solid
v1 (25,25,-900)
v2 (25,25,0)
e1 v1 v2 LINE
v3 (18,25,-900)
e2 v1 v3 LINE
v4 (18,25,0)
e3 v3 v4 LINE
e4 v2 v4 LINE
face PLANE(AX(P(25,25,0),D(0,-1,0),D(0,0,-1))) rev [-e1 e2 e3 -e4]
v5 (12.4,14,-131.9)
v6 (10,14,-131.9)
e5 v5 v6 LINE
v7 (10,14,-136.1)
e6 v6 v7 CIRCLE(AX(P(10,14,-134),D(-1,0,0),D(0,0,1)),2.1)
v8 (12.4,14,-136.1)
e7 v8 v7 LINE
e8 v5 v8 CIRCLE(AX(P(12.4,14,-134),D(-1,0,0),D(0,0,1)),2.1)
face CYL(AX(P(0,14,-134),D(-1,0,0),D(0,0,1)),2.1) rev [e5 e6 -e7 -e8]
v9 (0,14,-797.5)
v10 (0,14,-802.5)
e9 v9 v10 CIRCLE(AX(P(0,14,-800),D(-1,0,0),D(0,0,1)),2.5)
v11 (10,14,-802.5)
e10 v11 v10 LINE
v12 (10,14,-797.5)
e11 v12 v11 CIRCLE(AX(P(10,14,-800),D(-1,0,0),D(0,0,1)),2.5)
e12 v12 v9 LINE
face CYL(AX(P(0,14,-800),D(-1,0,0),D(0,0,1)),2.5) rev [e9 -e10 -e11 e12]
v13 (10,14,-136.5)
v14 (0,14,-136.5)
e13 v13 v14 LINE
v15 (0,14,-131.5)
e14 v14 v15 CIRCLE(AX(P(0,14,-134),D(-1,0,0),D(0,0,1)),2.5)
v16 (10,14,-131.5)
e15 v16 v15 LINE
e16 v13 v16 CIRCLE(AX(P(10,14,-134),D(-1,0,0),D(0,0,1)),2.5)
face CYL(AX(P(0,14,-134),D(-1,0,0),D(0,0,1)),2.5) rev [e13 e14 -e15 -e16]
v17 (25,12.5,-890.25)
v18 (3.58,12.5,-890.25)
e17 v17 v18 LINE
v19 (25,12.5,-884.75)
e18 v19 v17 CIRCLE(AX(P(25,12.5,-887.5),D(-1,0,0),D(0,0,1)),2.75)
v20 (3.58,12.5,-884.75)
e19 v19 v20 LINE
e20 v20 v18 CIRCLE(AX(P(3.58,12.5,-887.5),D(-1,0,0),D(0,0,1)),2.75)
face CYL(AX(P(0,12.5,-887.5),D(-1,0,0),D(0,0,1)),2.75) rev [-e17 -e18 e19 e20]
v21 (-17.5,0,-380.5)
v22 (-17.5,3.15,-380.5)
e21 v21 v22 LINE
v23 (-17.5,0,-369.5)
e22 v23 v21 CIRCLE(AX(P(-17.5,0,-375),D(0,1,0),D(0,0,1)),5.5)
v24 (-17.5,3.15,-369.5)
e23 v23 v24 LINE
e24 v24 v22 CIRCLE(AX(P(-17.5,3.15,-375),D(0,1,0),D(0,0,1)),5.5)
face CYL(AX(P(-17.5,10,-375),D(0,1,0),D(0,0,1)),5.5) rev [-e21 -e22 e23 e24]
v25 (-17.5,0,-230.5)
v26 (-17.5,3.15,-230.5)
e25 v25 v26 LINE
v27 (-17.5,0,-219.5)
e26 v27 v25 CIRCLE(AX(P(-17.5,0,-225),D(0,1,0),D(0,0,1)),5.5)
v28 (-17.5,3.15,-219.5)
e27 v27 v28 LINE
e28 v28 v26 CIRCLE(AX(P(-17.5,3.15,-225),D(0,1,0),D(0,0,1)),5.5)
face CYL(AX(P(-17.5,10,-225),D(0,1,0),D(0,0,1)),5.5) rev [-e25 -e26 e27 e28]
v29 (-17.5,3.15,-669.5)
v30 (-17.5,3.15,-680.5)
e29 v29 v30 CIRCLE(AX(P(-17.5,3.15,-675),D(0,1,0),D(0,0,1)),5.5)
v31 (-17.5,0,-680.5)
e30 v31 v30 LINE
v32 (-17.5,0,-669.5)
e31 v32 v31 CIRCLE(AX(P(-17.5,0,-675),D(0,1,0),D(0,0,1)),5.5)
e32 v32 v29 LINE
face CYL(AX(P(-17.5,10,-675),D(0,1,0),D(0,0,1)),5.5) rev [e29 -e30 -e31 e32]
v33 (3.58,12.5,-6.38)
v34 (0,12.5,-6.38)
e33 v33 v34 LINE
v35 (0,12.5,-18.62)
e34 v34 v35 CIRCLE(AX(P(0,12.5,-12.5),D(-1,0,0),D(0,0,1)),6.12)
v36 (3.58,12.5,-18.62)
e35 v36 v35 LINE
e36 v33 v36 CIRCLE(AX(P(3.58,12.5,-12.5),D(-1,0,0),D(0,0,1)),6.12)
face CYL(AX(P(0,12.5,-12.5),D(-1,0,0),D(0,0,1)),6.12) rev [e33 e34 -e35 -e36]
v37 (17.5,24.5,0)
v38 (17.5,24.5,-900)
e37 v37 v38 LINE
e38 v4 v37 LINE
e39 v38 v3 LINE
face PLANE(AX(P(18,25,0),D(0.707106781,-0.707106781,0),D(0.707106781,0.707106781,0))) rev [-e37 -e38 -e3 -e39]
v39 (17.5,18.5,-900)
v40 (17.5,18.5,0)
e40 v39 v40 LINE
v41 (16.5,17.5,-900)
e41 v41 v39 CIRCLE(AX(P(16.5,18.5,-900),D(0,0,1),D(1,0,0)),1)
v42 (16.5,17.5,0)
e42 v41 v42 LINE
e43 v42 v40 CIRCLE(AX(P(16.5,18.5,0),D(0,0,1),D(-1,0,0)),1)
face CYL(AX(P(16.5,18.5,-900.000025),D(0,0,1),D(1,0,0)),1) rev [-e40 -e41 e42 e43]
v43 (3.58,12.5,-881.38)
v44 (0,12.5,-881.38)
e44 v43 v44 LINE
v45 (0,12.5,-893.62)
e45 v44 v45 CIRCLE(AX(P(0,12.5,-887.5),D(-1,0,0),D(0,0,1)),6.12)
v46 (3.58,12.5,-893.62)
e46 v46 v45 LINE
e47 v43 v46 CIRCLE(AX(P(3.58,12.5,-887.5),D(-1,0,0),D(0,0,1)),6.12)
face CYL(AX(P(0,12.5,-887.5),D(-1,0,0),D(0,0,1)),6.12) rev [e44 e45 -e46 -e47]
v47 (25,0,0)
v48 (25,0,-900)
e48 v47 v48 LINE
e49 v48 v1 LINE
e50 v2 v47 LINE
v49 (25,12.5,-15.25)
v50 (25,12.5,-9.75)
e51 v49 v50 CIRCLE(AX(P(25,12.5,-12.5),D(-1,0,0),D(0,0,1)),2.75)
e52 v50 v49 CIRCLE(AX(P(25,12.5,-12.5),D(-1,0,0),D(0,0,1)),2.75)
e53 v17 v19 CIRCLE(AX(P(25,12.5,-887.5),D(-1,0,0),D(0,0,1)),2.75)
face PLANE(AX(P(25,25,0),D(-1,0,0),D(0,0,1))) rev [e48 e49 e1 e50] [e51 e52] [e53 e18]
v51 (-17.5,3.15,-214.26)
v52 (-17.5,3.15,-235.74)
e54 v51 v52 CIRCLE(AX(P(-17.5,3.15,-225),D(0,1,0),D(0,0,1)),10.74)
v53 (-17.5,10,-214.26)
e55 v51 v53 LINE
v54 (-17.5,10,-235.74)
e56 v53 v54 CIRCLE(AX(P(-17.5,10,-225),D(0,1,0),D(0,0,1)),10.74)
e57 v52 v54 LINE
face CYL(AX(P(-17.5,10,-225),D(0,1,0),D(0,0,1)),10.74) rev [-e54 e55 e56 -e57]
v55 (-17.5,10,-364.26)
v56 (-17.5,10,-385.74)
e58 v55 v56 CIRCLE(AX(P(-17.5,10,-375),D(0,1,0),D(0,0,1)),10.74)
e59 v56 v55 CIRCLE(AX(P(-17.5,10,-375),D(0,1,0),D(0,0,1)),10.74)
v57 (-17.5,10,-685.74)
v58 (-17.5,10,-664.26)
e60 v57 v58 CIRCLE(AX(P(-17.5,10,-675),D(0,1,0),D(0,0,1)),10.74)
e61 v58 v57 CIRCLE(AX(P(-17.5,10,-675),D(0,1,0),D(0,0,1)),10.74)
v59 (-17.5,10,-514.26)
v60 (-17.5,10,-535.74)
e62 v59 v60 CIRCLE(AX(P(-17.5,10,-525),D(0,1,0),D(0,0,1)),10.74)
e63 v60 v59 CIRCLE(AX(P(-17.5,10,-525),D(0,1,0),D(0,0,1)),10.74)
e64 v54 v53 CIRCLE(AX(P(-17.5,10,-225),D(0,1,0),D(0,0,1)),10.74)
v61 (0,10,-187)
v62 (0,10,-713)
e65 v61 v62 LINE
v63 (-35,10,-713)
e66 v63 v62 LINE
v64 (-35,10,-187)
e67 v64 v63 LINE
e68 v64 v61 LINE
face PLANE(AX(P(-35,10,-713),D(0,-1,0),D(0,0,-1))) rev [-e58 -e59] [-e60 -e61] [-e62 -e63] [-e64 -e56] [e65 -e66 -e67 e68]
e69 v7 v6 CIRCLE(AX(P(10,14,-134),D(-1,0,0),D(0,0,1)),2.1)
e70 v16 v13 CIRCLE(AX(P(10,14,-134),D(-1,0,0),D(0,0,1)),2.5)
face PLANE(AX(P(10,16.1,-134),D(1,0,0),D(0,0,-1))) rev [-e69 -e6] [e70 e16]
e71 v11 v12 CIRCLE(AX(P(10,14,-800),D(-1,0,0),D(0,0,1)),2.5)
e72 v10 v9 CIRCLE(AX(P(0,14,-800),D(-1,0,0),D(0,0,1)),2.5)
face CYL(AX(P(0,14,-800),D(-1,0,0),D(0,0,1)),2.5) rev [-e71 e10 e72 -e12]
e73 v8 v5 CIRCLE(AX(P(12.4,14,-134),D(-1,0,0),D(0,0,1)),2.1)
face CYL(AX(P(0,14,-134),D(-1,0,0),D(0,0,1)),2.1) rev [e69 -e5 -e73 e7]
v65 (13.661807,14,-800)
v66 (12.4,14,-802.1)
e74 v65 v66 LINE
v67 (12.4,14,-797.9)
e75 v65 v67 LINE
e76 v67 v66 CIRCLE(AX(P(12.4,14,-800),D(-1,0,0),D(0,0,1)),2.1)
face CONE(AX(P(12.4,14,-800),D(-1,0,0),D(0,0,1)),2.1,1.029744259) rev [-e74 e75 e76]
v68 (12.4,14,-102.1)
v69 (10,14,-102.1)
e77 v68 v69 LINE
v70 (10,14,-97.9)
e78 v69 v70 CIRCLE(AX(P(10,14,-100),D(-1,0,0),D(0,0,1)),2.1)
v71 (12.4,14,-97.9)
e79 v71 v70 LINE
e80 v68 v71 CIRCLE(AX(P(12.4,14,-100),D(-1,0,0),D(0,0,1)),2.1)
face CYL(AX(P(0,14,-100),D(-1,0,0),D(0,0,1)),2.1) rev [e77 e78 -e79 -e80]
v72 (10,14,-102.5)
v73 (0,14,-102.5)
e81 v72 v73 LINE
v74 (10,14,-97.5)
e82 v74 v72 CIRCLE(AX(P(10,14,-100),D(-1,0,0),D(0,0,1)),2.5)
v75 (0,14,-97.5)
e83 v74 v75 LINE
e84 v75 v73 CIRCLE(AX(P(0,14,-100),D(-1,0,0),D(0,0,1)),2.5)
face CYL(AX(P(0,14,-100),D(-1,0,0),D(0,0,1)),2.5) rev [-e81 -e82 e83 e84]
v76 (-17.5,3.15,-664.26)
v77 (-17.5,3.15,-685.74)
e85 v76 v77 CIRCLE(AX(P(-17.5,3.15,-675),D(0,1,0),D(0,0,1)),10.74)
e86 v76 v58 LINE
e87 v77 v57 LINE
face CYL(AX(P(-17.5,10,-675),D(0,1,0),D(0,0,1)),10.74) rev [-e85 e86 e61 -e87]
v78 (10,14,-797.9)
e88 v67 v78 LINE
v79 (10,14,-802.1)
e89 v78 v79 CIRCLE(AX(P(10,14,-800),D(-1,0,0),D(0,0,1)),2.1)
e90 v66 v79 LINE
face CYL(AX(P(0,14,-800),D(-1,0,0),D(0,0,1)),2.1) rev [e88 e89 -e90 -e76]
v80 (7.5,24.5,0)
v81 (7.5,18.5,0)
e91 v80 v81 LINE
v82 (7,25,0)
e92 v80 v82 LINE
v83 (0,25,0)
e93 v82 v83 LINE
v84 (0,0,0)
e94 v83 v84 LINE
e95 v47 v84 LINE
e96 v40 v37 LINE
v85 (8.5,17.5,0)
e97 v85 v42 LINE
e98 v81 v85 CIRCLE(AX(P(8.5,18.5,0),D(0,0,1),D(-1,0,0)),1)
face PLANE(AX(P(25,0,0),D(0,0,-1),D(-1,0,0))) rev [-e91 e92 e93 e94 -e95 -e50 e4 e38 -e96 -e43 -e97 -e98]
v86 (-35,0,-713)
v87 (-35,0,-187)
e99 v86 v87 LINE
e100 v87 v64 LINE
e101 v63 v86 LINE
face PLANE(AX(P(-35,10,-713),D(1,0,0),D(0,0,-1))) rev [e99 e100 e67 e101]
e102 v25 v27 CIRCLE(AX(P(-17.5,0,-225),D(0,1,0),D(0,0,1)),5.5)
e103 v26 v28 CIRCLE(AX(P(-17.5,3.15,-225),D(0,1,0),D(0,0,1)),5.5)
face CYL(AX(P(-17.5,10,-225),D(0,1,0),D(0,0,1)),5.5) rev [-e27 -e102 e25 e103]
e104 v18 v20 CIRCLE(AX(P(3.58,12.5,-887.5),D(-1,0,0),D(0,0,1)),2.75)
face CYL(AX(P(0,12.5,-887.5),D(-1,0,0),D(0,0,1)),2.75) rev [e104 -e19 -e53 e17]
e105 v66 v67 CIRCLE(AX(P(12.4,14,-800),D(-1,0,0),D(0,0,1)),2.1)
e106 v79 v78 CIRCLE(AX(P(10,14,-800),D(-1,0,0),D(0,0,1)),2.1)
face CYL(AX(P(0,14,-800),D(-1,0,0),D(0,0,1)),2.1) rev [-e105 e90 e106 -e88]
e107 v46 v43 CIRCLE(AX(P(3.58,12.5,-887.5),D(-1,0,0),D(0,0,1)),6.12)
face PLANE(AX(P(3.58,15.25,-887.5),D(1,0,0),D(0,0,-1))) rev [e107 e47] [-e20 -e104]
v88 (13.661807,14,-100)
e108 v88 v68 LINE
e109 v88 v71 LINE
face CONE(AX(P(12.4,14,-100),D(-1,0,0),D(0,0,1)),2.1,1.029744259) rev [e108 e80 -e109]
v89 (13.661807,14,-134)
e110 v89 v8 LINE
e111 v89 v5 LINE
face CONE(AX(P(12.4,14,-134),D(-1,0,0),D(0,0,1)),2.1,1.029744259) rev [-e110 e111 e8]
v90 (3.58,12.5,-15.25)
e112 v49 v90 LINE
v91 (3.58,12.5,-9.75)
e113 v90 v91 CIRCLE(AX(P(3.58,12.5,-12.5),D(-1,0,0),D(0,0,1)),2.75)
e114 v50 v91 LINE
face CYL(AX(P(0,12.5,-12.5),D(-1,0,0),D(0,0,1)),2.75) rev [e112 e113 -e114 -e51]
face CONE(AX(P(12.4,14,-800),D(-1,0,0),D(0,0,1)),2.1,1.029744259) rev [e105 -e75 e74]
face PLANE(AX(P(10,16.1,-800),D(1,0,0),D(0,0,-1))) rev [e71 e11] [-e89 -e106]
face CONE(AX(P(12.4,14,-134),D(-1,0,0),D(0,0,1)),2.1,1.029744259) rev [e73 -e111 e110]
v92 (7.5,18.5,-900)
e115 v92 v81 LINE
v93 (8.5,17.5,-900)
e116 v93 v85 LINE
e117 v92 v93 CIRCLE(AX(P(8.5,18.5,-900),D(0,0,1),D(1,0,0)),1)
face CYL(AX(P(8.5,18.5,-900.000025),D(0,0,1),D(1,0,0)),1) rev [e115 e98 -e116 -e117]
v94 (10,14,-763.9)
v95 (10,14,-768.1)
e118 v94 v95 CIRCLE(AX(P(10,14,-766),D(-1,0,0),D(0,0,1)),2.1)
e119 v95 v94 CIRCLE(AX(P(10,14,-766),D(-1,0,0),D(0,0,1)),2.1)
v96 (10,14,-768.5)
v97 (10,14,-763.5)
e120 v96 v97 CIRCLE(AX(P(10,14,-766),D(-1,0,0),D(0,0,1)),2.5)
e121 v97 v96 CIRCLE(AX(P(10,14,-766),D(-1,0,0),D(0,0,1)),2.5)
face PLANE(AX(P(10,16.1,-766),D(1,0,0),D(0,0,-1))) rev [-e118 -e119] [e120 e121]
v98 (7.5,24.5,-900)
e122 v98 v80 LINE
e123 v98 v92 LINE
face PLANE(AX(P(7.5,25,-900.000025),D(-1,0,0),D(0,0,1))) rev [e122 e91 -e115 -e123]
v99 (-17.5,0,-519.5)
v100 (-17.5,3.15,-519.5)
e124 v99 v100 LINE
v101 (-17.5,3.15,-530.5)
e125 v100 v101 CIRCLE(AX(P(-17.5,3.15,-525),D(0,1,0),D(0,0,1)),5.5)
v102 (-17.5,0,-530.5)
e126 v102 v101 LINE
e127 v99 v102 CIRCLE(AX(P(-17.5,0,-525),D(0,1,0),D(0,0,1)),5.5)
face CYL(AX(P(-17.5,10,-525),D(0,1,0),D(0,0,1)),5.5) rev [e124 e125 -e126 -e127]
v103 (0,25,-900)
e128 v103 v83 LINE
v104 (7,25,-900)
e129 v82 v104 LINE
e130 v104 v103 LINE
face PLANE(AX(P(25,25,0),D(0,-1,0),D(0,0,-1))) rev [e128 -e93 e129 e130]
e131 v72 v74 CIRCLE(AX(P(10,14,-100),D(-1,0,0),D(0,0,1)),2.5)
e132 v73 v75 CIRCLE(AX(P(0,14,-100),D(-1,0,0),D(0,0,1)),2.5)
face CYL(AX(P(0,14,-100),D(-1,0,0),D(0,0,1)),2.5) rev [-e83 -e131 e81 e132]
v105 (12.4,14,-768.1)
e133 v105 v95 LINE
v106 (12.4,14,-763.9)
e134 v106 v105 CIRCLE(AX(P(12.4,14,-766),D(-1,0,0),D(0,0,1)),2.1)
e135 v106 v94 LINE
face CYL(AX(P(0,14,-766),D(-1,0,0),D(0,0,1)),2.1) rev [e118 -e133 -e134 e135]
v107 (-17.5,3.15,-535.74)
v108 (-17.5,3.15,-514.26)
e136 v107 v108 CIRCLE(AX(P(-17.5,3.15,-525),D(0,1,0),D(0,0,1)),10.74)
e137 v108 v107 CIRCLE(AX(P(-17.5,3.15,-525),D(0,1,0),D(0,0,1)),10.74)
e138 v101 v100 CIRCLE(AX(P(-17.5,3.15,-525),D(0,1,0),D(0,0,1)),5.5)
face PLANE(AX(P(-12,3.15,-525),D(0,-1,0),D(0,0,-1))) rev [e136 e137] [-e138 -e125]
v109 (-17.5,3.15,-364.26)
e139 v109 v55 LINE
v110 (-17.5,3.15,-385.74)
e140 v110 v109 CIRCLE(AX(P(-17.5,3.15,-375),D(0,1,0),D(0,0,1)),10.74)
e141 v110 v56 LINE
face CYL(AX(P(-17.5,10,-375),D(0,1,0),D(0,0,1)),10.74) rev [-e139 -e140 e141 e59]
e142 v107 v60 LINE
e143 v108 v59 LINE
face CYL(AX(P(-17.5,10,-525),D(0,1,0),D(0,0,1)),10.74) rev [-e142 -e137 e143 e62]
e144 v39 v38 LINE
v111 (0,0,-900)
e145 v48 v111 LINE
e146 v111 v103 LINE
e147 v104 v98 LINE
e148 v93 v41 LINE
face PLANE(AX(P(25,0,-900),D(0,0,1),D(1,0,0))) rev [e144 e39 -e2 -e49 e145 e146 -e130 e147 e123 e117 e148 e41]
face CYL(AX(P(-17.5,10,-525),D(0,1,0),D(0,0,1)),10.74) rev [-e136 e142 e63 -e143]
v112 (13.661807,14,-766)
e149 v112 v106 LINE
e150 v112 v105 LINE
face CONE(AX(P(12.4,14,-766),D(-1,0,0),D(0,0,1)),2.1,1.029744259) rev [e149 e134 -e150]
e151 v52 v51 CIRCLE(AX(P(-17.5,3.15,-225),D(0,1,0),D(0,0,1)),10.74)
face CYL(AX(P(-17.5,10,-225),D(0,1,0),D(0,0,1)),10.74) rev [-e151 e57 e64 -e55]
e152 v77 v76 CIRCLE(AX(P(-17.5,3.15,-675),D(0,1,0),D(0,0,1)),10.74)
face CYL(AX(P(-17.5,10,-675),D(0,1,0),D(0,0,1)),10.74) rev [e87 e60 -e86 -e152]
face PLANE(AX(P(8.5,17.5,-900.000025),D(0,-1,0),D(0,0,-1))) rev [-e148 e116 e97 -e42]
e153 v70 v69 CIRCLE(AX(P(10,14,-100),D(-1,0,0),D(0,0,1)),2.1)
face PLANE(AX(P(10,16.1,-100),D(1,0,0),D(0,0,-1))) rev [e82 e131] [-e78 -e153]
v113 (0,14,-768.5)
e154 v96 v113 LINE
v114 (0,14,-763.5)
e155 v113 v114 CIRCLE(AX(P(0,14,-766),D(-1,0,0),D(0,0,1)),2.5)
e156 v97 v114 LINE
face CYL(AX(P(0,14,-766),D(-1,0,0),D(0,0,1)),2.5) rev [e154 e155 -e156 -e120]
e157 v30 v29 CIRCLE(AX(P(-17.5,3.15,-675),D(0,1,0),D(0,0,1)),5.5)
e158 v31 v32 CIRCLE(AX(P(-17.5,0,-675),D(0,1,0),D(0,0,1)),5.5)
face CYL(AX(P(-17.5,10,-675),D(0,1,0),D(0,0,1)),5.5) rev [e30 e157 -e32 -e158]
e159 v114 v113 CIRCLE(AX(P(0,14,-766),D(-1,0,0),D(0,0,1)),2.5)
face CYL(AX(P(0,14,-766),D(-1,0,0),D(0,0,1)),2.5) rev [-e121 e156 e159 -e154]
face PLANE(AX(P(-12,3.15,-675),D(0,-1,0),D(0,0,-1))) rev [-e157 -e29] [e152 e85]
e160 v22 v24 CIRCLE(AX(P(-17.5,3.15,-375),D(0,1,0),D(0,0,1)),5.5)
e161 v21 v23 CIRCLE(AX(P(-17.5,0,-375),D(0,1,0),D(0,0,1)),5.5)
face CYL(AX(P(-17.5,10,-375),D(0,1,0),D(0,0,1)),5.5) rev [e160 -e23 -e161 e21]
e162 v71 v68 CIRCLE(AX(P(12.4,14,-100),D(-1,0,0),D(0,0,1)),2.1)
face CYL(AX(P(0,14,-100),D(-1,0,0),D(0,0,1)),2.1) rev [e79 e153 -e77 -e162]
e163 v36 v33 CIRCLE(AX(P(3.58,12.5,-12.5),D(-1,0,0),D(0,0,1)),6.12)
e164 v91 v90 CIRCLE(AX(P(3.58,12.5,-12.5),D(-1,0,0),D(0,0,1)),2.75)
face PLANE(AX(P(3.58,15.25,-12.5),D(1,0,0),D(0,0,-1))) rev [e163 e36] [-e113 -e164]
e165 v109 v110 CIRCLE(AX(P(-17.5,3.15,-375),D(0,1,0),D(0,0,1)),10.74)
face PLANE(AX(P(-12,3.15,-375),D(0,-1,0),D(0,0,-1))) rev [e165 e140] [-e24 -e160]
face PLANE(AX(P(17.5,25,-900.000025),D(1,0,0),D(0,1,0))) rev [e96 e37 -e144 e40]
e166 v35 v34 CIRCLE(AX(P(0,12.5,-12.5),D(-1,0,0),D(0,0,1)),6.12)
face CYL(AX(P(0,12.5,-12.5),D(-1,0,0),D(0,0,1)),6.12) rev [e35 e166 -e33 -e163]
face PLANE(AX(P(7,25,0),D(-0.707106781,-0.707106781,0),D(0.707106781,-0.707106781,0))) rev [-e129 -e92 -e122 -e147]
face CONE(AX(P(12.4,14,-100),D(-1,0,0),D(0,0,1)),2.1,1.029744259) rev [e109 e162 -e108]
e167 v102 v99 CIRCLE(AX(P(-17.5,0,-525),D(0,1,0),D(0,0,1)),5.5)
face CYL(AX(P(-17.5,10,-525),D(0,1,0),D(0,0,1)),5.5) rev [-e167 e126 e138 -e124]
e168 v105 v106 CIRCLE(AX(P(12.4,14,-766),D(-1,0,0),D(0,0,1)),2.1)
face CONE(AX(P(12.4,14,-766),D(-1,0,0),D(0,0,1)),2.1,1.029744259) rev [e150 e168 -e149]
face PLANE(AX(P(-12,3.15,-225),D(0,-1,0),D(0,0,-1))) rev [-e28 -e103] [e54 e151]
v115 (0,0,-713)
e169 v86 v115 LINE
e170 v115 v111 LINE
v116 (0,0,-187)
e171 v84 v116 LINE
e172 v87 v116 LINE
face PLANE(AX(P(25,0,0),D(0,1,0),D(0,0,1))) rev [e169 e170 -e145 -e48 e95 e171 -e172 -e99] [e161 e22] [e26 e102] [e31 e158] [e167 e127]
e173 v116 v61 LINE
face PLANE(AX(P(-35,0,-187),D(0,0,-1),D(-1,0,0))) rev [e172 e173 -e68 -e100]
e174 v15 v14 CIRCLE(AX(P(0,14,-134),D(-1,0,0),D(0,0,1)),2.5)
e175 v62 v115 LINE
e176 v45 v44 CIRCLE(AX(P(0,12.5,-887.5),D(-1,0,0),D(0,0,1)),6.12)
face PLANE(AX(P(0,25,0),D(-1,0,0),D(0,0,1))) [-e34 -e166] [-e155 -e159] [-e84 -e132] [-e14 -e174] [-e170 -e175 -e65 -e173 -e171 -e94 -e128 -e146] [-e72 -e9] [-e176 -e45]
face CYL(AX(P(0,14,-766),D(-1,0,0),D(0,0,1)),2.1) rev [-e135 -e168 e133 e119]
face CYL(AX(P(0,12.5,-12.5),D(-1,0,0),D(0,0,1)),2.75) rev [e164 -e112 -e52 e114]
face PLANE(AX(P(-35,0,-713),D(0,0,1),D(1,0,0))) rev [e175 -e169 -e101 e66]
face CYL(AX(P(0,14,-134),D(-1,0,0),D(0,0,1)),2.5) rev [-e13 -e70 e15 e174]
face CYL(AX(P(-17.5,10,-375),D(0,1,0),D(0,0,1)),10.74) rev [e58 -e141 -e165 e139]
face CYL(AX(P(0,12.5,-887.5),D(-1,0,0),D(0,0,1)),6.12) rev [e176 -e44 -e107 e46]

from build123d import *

# Parameters (mm, degrees)
SKETCH_1_W                    = 900
SKETCH_1_H                    = 25
EXTRUDE_1_DEPTH               = 25
SKETCH_2_W                    = 526
SKETCH_2_H                    = 10
EXTRUDE_2_DEPTH               = 35
CUT_EXTRUDE_1_DEPTH           = 902.027191599
CHAMFER_1_SIZE                = 0.5
HOLE_WIZARD_M10_1_D           = 11
HOLE_WIZARD_M10_1_CBORE_D     = 21.48
HOLE_WIZARD_M10_1_CBORE_DEPTH = 6.85
HOLE_WIZARD_M5_1_D            = 5.5
HOLE_WIZARD_M5_1_CBORE_D      = 12.24
HOLE_WIZARD_M5_1_CBORE_DEPTH  = 3.58
HOLE_WIZARD_M5_1_2_AT_2_COUNT = 2
HOLE_WIZARD_M5_1_2_AT_2_PITCH = 34
PATTERN_LINEAR_1_COUNT        = 2
PATTERN_LINEAR_1_PITCH        = 666


with BuildPart() as part:
    # 草图1 → 拉伸1 (new body)
    with BuildSketch(Plane(origin=(0, 0, 0), x_dir=(0, 0, -1), z_dir=(1, 0, 0))):
        with Locations((450, 12.5)):
            Rectangle(SKETCH_1_W, SKETCH_1_H)
    extrude(amount=EXTRUDE_1_DEPTH)

    # 草图2 → 拉伸2 (add)
    with BuildSketch(Plane.ZY):
        with Locations((-450, 5)):
            Rectangle(SKETCH_2_W, SKETCH_2_H)
    extrude(amount=EXTRUDE_2_DEPTH)

    # 草图3 → 切除-拉伸1 (cut, through all)
    with BuildSketch(Plane.XY):
        with BuildLine():
            Line((7.5, 25), (17.5, 25))
            Line((17.5, 25), (17.5, 18.5))
            ThreePointArc((17.5, 18.5), (17.207106781, 17.792893219), (16.5, 17.5))
            Line((16.5, 17.5), (8.5, 17.5))
            ThreePointArc((8.5, 17.5), (7.792893219, 17.792893219), (7.5, 18.5))
            Line((7.5, 18.5), (7.5, 25))
        make_face()
    extrude(amount=-CUT_EXTRUDE_1_DEPTH, mode=Mode.SUBTRACT)

    # 倒角1
    chamfer_1_edges = [part.edges().sort_by_distance(p)[0] for p in [
        (17.5, 25, -450),
        (7.5, 25, -450),
    ]]
    chamfer(chamfer_1_edges, length=CHAMFER_1_SIZE)

    # M10 六角头螺栓的柱形沉头孔1 (through all)
    with Locations(Plane(origin=(-17.5, 10, -675), x_dir=(0, 0, 1), z_dir=(0, 1, 0))):
        with Locations((0, 0), (150.000000001, 0), (300.000000001, 0), (450, 0)):
            CounterBoreHole(HOLE_WIZARD_M10_1_D / 2, HOLE_WIZARD_M10_1_CBORE_D / 2, HOLE_WIZARD_M10_1_CBORE_DEPTH)

    # Hole Wizard M5 _1 (through all)
    with Locations(Plane(origin=(0, 12.5, -887.5), x_dir=(0, 0, -1), z_dir=(-1, 0, 0))):
        with Locations((0, 0), (-875, 0)):
            CounterBoreHole(HOLE_WIZARD_M5_1_D / 2, HOLE_WIZARD_M5_1_CBORE_D / 2, HOLE_WIZARD_M5_1_CBORE_DEPTH)

    # 草图8 → Hole Wizard M5 _1 2 (revolve, cut)
    with BuildSketch(Plane(origin=(0, 14, -800), x_dir=(0, 0, 1), z_dir=(0, 1, 0))):
        Polygon((0, 0), (0, 13.6618073), (2.1, 12.4), (2.1, 10), (2.5, 10), (2.5, 0), align=None)
    hole_wizard_m5_1_2 = revolve(axis=Axis((-6.35, 14, -800), (1, 0, 0)), mode=Mode.SUBTRACT)

    # Hole Wizard M5 _1 2 at 2: Hole Wizard M5 _1 2 ×2
    with Locations(*[(0, 0, i * HOLE_WIZARD_M5_1_2_AT_2_PITCH) for i in range(1, HOLE_WIZARD_M5_1_2_AT_2_COUNT)]):
        add(hole_wizard_m5_1_2, mode=Mode.SUBTRACT)

    # 阵列(线性)1: Hole Wizard M5 _1 2 ×2
    with Locations(*[(0, 0, i * PATTERN_LINEAR_1_PITCH) for i in range(1, PATTERN_LINEAR_1_COUNT)]):
        add(hole_wizard_m5_1_2, mode=Mode.SUBTRACT)

    # 阵列(线性)1 copy 1 sketch → 阵列(线性)1 copy 1 (revolve, cut)
    with BuildSketch(Plane(origin=(0, 14, -100), x_dir=(0, 0, 1), z_dir=(0, 1, 0))):
        Polygon((0, 0), (0, 13.6618073), (2.1, 12.4), (2.1, 10), (2.5, 10), (2.5, 0), align=None)
    revolve(axis=Axis((-6.35, 14, -100), (1, 0, 0)), mode=Mode.SUBTRACT)


solid = part.part
